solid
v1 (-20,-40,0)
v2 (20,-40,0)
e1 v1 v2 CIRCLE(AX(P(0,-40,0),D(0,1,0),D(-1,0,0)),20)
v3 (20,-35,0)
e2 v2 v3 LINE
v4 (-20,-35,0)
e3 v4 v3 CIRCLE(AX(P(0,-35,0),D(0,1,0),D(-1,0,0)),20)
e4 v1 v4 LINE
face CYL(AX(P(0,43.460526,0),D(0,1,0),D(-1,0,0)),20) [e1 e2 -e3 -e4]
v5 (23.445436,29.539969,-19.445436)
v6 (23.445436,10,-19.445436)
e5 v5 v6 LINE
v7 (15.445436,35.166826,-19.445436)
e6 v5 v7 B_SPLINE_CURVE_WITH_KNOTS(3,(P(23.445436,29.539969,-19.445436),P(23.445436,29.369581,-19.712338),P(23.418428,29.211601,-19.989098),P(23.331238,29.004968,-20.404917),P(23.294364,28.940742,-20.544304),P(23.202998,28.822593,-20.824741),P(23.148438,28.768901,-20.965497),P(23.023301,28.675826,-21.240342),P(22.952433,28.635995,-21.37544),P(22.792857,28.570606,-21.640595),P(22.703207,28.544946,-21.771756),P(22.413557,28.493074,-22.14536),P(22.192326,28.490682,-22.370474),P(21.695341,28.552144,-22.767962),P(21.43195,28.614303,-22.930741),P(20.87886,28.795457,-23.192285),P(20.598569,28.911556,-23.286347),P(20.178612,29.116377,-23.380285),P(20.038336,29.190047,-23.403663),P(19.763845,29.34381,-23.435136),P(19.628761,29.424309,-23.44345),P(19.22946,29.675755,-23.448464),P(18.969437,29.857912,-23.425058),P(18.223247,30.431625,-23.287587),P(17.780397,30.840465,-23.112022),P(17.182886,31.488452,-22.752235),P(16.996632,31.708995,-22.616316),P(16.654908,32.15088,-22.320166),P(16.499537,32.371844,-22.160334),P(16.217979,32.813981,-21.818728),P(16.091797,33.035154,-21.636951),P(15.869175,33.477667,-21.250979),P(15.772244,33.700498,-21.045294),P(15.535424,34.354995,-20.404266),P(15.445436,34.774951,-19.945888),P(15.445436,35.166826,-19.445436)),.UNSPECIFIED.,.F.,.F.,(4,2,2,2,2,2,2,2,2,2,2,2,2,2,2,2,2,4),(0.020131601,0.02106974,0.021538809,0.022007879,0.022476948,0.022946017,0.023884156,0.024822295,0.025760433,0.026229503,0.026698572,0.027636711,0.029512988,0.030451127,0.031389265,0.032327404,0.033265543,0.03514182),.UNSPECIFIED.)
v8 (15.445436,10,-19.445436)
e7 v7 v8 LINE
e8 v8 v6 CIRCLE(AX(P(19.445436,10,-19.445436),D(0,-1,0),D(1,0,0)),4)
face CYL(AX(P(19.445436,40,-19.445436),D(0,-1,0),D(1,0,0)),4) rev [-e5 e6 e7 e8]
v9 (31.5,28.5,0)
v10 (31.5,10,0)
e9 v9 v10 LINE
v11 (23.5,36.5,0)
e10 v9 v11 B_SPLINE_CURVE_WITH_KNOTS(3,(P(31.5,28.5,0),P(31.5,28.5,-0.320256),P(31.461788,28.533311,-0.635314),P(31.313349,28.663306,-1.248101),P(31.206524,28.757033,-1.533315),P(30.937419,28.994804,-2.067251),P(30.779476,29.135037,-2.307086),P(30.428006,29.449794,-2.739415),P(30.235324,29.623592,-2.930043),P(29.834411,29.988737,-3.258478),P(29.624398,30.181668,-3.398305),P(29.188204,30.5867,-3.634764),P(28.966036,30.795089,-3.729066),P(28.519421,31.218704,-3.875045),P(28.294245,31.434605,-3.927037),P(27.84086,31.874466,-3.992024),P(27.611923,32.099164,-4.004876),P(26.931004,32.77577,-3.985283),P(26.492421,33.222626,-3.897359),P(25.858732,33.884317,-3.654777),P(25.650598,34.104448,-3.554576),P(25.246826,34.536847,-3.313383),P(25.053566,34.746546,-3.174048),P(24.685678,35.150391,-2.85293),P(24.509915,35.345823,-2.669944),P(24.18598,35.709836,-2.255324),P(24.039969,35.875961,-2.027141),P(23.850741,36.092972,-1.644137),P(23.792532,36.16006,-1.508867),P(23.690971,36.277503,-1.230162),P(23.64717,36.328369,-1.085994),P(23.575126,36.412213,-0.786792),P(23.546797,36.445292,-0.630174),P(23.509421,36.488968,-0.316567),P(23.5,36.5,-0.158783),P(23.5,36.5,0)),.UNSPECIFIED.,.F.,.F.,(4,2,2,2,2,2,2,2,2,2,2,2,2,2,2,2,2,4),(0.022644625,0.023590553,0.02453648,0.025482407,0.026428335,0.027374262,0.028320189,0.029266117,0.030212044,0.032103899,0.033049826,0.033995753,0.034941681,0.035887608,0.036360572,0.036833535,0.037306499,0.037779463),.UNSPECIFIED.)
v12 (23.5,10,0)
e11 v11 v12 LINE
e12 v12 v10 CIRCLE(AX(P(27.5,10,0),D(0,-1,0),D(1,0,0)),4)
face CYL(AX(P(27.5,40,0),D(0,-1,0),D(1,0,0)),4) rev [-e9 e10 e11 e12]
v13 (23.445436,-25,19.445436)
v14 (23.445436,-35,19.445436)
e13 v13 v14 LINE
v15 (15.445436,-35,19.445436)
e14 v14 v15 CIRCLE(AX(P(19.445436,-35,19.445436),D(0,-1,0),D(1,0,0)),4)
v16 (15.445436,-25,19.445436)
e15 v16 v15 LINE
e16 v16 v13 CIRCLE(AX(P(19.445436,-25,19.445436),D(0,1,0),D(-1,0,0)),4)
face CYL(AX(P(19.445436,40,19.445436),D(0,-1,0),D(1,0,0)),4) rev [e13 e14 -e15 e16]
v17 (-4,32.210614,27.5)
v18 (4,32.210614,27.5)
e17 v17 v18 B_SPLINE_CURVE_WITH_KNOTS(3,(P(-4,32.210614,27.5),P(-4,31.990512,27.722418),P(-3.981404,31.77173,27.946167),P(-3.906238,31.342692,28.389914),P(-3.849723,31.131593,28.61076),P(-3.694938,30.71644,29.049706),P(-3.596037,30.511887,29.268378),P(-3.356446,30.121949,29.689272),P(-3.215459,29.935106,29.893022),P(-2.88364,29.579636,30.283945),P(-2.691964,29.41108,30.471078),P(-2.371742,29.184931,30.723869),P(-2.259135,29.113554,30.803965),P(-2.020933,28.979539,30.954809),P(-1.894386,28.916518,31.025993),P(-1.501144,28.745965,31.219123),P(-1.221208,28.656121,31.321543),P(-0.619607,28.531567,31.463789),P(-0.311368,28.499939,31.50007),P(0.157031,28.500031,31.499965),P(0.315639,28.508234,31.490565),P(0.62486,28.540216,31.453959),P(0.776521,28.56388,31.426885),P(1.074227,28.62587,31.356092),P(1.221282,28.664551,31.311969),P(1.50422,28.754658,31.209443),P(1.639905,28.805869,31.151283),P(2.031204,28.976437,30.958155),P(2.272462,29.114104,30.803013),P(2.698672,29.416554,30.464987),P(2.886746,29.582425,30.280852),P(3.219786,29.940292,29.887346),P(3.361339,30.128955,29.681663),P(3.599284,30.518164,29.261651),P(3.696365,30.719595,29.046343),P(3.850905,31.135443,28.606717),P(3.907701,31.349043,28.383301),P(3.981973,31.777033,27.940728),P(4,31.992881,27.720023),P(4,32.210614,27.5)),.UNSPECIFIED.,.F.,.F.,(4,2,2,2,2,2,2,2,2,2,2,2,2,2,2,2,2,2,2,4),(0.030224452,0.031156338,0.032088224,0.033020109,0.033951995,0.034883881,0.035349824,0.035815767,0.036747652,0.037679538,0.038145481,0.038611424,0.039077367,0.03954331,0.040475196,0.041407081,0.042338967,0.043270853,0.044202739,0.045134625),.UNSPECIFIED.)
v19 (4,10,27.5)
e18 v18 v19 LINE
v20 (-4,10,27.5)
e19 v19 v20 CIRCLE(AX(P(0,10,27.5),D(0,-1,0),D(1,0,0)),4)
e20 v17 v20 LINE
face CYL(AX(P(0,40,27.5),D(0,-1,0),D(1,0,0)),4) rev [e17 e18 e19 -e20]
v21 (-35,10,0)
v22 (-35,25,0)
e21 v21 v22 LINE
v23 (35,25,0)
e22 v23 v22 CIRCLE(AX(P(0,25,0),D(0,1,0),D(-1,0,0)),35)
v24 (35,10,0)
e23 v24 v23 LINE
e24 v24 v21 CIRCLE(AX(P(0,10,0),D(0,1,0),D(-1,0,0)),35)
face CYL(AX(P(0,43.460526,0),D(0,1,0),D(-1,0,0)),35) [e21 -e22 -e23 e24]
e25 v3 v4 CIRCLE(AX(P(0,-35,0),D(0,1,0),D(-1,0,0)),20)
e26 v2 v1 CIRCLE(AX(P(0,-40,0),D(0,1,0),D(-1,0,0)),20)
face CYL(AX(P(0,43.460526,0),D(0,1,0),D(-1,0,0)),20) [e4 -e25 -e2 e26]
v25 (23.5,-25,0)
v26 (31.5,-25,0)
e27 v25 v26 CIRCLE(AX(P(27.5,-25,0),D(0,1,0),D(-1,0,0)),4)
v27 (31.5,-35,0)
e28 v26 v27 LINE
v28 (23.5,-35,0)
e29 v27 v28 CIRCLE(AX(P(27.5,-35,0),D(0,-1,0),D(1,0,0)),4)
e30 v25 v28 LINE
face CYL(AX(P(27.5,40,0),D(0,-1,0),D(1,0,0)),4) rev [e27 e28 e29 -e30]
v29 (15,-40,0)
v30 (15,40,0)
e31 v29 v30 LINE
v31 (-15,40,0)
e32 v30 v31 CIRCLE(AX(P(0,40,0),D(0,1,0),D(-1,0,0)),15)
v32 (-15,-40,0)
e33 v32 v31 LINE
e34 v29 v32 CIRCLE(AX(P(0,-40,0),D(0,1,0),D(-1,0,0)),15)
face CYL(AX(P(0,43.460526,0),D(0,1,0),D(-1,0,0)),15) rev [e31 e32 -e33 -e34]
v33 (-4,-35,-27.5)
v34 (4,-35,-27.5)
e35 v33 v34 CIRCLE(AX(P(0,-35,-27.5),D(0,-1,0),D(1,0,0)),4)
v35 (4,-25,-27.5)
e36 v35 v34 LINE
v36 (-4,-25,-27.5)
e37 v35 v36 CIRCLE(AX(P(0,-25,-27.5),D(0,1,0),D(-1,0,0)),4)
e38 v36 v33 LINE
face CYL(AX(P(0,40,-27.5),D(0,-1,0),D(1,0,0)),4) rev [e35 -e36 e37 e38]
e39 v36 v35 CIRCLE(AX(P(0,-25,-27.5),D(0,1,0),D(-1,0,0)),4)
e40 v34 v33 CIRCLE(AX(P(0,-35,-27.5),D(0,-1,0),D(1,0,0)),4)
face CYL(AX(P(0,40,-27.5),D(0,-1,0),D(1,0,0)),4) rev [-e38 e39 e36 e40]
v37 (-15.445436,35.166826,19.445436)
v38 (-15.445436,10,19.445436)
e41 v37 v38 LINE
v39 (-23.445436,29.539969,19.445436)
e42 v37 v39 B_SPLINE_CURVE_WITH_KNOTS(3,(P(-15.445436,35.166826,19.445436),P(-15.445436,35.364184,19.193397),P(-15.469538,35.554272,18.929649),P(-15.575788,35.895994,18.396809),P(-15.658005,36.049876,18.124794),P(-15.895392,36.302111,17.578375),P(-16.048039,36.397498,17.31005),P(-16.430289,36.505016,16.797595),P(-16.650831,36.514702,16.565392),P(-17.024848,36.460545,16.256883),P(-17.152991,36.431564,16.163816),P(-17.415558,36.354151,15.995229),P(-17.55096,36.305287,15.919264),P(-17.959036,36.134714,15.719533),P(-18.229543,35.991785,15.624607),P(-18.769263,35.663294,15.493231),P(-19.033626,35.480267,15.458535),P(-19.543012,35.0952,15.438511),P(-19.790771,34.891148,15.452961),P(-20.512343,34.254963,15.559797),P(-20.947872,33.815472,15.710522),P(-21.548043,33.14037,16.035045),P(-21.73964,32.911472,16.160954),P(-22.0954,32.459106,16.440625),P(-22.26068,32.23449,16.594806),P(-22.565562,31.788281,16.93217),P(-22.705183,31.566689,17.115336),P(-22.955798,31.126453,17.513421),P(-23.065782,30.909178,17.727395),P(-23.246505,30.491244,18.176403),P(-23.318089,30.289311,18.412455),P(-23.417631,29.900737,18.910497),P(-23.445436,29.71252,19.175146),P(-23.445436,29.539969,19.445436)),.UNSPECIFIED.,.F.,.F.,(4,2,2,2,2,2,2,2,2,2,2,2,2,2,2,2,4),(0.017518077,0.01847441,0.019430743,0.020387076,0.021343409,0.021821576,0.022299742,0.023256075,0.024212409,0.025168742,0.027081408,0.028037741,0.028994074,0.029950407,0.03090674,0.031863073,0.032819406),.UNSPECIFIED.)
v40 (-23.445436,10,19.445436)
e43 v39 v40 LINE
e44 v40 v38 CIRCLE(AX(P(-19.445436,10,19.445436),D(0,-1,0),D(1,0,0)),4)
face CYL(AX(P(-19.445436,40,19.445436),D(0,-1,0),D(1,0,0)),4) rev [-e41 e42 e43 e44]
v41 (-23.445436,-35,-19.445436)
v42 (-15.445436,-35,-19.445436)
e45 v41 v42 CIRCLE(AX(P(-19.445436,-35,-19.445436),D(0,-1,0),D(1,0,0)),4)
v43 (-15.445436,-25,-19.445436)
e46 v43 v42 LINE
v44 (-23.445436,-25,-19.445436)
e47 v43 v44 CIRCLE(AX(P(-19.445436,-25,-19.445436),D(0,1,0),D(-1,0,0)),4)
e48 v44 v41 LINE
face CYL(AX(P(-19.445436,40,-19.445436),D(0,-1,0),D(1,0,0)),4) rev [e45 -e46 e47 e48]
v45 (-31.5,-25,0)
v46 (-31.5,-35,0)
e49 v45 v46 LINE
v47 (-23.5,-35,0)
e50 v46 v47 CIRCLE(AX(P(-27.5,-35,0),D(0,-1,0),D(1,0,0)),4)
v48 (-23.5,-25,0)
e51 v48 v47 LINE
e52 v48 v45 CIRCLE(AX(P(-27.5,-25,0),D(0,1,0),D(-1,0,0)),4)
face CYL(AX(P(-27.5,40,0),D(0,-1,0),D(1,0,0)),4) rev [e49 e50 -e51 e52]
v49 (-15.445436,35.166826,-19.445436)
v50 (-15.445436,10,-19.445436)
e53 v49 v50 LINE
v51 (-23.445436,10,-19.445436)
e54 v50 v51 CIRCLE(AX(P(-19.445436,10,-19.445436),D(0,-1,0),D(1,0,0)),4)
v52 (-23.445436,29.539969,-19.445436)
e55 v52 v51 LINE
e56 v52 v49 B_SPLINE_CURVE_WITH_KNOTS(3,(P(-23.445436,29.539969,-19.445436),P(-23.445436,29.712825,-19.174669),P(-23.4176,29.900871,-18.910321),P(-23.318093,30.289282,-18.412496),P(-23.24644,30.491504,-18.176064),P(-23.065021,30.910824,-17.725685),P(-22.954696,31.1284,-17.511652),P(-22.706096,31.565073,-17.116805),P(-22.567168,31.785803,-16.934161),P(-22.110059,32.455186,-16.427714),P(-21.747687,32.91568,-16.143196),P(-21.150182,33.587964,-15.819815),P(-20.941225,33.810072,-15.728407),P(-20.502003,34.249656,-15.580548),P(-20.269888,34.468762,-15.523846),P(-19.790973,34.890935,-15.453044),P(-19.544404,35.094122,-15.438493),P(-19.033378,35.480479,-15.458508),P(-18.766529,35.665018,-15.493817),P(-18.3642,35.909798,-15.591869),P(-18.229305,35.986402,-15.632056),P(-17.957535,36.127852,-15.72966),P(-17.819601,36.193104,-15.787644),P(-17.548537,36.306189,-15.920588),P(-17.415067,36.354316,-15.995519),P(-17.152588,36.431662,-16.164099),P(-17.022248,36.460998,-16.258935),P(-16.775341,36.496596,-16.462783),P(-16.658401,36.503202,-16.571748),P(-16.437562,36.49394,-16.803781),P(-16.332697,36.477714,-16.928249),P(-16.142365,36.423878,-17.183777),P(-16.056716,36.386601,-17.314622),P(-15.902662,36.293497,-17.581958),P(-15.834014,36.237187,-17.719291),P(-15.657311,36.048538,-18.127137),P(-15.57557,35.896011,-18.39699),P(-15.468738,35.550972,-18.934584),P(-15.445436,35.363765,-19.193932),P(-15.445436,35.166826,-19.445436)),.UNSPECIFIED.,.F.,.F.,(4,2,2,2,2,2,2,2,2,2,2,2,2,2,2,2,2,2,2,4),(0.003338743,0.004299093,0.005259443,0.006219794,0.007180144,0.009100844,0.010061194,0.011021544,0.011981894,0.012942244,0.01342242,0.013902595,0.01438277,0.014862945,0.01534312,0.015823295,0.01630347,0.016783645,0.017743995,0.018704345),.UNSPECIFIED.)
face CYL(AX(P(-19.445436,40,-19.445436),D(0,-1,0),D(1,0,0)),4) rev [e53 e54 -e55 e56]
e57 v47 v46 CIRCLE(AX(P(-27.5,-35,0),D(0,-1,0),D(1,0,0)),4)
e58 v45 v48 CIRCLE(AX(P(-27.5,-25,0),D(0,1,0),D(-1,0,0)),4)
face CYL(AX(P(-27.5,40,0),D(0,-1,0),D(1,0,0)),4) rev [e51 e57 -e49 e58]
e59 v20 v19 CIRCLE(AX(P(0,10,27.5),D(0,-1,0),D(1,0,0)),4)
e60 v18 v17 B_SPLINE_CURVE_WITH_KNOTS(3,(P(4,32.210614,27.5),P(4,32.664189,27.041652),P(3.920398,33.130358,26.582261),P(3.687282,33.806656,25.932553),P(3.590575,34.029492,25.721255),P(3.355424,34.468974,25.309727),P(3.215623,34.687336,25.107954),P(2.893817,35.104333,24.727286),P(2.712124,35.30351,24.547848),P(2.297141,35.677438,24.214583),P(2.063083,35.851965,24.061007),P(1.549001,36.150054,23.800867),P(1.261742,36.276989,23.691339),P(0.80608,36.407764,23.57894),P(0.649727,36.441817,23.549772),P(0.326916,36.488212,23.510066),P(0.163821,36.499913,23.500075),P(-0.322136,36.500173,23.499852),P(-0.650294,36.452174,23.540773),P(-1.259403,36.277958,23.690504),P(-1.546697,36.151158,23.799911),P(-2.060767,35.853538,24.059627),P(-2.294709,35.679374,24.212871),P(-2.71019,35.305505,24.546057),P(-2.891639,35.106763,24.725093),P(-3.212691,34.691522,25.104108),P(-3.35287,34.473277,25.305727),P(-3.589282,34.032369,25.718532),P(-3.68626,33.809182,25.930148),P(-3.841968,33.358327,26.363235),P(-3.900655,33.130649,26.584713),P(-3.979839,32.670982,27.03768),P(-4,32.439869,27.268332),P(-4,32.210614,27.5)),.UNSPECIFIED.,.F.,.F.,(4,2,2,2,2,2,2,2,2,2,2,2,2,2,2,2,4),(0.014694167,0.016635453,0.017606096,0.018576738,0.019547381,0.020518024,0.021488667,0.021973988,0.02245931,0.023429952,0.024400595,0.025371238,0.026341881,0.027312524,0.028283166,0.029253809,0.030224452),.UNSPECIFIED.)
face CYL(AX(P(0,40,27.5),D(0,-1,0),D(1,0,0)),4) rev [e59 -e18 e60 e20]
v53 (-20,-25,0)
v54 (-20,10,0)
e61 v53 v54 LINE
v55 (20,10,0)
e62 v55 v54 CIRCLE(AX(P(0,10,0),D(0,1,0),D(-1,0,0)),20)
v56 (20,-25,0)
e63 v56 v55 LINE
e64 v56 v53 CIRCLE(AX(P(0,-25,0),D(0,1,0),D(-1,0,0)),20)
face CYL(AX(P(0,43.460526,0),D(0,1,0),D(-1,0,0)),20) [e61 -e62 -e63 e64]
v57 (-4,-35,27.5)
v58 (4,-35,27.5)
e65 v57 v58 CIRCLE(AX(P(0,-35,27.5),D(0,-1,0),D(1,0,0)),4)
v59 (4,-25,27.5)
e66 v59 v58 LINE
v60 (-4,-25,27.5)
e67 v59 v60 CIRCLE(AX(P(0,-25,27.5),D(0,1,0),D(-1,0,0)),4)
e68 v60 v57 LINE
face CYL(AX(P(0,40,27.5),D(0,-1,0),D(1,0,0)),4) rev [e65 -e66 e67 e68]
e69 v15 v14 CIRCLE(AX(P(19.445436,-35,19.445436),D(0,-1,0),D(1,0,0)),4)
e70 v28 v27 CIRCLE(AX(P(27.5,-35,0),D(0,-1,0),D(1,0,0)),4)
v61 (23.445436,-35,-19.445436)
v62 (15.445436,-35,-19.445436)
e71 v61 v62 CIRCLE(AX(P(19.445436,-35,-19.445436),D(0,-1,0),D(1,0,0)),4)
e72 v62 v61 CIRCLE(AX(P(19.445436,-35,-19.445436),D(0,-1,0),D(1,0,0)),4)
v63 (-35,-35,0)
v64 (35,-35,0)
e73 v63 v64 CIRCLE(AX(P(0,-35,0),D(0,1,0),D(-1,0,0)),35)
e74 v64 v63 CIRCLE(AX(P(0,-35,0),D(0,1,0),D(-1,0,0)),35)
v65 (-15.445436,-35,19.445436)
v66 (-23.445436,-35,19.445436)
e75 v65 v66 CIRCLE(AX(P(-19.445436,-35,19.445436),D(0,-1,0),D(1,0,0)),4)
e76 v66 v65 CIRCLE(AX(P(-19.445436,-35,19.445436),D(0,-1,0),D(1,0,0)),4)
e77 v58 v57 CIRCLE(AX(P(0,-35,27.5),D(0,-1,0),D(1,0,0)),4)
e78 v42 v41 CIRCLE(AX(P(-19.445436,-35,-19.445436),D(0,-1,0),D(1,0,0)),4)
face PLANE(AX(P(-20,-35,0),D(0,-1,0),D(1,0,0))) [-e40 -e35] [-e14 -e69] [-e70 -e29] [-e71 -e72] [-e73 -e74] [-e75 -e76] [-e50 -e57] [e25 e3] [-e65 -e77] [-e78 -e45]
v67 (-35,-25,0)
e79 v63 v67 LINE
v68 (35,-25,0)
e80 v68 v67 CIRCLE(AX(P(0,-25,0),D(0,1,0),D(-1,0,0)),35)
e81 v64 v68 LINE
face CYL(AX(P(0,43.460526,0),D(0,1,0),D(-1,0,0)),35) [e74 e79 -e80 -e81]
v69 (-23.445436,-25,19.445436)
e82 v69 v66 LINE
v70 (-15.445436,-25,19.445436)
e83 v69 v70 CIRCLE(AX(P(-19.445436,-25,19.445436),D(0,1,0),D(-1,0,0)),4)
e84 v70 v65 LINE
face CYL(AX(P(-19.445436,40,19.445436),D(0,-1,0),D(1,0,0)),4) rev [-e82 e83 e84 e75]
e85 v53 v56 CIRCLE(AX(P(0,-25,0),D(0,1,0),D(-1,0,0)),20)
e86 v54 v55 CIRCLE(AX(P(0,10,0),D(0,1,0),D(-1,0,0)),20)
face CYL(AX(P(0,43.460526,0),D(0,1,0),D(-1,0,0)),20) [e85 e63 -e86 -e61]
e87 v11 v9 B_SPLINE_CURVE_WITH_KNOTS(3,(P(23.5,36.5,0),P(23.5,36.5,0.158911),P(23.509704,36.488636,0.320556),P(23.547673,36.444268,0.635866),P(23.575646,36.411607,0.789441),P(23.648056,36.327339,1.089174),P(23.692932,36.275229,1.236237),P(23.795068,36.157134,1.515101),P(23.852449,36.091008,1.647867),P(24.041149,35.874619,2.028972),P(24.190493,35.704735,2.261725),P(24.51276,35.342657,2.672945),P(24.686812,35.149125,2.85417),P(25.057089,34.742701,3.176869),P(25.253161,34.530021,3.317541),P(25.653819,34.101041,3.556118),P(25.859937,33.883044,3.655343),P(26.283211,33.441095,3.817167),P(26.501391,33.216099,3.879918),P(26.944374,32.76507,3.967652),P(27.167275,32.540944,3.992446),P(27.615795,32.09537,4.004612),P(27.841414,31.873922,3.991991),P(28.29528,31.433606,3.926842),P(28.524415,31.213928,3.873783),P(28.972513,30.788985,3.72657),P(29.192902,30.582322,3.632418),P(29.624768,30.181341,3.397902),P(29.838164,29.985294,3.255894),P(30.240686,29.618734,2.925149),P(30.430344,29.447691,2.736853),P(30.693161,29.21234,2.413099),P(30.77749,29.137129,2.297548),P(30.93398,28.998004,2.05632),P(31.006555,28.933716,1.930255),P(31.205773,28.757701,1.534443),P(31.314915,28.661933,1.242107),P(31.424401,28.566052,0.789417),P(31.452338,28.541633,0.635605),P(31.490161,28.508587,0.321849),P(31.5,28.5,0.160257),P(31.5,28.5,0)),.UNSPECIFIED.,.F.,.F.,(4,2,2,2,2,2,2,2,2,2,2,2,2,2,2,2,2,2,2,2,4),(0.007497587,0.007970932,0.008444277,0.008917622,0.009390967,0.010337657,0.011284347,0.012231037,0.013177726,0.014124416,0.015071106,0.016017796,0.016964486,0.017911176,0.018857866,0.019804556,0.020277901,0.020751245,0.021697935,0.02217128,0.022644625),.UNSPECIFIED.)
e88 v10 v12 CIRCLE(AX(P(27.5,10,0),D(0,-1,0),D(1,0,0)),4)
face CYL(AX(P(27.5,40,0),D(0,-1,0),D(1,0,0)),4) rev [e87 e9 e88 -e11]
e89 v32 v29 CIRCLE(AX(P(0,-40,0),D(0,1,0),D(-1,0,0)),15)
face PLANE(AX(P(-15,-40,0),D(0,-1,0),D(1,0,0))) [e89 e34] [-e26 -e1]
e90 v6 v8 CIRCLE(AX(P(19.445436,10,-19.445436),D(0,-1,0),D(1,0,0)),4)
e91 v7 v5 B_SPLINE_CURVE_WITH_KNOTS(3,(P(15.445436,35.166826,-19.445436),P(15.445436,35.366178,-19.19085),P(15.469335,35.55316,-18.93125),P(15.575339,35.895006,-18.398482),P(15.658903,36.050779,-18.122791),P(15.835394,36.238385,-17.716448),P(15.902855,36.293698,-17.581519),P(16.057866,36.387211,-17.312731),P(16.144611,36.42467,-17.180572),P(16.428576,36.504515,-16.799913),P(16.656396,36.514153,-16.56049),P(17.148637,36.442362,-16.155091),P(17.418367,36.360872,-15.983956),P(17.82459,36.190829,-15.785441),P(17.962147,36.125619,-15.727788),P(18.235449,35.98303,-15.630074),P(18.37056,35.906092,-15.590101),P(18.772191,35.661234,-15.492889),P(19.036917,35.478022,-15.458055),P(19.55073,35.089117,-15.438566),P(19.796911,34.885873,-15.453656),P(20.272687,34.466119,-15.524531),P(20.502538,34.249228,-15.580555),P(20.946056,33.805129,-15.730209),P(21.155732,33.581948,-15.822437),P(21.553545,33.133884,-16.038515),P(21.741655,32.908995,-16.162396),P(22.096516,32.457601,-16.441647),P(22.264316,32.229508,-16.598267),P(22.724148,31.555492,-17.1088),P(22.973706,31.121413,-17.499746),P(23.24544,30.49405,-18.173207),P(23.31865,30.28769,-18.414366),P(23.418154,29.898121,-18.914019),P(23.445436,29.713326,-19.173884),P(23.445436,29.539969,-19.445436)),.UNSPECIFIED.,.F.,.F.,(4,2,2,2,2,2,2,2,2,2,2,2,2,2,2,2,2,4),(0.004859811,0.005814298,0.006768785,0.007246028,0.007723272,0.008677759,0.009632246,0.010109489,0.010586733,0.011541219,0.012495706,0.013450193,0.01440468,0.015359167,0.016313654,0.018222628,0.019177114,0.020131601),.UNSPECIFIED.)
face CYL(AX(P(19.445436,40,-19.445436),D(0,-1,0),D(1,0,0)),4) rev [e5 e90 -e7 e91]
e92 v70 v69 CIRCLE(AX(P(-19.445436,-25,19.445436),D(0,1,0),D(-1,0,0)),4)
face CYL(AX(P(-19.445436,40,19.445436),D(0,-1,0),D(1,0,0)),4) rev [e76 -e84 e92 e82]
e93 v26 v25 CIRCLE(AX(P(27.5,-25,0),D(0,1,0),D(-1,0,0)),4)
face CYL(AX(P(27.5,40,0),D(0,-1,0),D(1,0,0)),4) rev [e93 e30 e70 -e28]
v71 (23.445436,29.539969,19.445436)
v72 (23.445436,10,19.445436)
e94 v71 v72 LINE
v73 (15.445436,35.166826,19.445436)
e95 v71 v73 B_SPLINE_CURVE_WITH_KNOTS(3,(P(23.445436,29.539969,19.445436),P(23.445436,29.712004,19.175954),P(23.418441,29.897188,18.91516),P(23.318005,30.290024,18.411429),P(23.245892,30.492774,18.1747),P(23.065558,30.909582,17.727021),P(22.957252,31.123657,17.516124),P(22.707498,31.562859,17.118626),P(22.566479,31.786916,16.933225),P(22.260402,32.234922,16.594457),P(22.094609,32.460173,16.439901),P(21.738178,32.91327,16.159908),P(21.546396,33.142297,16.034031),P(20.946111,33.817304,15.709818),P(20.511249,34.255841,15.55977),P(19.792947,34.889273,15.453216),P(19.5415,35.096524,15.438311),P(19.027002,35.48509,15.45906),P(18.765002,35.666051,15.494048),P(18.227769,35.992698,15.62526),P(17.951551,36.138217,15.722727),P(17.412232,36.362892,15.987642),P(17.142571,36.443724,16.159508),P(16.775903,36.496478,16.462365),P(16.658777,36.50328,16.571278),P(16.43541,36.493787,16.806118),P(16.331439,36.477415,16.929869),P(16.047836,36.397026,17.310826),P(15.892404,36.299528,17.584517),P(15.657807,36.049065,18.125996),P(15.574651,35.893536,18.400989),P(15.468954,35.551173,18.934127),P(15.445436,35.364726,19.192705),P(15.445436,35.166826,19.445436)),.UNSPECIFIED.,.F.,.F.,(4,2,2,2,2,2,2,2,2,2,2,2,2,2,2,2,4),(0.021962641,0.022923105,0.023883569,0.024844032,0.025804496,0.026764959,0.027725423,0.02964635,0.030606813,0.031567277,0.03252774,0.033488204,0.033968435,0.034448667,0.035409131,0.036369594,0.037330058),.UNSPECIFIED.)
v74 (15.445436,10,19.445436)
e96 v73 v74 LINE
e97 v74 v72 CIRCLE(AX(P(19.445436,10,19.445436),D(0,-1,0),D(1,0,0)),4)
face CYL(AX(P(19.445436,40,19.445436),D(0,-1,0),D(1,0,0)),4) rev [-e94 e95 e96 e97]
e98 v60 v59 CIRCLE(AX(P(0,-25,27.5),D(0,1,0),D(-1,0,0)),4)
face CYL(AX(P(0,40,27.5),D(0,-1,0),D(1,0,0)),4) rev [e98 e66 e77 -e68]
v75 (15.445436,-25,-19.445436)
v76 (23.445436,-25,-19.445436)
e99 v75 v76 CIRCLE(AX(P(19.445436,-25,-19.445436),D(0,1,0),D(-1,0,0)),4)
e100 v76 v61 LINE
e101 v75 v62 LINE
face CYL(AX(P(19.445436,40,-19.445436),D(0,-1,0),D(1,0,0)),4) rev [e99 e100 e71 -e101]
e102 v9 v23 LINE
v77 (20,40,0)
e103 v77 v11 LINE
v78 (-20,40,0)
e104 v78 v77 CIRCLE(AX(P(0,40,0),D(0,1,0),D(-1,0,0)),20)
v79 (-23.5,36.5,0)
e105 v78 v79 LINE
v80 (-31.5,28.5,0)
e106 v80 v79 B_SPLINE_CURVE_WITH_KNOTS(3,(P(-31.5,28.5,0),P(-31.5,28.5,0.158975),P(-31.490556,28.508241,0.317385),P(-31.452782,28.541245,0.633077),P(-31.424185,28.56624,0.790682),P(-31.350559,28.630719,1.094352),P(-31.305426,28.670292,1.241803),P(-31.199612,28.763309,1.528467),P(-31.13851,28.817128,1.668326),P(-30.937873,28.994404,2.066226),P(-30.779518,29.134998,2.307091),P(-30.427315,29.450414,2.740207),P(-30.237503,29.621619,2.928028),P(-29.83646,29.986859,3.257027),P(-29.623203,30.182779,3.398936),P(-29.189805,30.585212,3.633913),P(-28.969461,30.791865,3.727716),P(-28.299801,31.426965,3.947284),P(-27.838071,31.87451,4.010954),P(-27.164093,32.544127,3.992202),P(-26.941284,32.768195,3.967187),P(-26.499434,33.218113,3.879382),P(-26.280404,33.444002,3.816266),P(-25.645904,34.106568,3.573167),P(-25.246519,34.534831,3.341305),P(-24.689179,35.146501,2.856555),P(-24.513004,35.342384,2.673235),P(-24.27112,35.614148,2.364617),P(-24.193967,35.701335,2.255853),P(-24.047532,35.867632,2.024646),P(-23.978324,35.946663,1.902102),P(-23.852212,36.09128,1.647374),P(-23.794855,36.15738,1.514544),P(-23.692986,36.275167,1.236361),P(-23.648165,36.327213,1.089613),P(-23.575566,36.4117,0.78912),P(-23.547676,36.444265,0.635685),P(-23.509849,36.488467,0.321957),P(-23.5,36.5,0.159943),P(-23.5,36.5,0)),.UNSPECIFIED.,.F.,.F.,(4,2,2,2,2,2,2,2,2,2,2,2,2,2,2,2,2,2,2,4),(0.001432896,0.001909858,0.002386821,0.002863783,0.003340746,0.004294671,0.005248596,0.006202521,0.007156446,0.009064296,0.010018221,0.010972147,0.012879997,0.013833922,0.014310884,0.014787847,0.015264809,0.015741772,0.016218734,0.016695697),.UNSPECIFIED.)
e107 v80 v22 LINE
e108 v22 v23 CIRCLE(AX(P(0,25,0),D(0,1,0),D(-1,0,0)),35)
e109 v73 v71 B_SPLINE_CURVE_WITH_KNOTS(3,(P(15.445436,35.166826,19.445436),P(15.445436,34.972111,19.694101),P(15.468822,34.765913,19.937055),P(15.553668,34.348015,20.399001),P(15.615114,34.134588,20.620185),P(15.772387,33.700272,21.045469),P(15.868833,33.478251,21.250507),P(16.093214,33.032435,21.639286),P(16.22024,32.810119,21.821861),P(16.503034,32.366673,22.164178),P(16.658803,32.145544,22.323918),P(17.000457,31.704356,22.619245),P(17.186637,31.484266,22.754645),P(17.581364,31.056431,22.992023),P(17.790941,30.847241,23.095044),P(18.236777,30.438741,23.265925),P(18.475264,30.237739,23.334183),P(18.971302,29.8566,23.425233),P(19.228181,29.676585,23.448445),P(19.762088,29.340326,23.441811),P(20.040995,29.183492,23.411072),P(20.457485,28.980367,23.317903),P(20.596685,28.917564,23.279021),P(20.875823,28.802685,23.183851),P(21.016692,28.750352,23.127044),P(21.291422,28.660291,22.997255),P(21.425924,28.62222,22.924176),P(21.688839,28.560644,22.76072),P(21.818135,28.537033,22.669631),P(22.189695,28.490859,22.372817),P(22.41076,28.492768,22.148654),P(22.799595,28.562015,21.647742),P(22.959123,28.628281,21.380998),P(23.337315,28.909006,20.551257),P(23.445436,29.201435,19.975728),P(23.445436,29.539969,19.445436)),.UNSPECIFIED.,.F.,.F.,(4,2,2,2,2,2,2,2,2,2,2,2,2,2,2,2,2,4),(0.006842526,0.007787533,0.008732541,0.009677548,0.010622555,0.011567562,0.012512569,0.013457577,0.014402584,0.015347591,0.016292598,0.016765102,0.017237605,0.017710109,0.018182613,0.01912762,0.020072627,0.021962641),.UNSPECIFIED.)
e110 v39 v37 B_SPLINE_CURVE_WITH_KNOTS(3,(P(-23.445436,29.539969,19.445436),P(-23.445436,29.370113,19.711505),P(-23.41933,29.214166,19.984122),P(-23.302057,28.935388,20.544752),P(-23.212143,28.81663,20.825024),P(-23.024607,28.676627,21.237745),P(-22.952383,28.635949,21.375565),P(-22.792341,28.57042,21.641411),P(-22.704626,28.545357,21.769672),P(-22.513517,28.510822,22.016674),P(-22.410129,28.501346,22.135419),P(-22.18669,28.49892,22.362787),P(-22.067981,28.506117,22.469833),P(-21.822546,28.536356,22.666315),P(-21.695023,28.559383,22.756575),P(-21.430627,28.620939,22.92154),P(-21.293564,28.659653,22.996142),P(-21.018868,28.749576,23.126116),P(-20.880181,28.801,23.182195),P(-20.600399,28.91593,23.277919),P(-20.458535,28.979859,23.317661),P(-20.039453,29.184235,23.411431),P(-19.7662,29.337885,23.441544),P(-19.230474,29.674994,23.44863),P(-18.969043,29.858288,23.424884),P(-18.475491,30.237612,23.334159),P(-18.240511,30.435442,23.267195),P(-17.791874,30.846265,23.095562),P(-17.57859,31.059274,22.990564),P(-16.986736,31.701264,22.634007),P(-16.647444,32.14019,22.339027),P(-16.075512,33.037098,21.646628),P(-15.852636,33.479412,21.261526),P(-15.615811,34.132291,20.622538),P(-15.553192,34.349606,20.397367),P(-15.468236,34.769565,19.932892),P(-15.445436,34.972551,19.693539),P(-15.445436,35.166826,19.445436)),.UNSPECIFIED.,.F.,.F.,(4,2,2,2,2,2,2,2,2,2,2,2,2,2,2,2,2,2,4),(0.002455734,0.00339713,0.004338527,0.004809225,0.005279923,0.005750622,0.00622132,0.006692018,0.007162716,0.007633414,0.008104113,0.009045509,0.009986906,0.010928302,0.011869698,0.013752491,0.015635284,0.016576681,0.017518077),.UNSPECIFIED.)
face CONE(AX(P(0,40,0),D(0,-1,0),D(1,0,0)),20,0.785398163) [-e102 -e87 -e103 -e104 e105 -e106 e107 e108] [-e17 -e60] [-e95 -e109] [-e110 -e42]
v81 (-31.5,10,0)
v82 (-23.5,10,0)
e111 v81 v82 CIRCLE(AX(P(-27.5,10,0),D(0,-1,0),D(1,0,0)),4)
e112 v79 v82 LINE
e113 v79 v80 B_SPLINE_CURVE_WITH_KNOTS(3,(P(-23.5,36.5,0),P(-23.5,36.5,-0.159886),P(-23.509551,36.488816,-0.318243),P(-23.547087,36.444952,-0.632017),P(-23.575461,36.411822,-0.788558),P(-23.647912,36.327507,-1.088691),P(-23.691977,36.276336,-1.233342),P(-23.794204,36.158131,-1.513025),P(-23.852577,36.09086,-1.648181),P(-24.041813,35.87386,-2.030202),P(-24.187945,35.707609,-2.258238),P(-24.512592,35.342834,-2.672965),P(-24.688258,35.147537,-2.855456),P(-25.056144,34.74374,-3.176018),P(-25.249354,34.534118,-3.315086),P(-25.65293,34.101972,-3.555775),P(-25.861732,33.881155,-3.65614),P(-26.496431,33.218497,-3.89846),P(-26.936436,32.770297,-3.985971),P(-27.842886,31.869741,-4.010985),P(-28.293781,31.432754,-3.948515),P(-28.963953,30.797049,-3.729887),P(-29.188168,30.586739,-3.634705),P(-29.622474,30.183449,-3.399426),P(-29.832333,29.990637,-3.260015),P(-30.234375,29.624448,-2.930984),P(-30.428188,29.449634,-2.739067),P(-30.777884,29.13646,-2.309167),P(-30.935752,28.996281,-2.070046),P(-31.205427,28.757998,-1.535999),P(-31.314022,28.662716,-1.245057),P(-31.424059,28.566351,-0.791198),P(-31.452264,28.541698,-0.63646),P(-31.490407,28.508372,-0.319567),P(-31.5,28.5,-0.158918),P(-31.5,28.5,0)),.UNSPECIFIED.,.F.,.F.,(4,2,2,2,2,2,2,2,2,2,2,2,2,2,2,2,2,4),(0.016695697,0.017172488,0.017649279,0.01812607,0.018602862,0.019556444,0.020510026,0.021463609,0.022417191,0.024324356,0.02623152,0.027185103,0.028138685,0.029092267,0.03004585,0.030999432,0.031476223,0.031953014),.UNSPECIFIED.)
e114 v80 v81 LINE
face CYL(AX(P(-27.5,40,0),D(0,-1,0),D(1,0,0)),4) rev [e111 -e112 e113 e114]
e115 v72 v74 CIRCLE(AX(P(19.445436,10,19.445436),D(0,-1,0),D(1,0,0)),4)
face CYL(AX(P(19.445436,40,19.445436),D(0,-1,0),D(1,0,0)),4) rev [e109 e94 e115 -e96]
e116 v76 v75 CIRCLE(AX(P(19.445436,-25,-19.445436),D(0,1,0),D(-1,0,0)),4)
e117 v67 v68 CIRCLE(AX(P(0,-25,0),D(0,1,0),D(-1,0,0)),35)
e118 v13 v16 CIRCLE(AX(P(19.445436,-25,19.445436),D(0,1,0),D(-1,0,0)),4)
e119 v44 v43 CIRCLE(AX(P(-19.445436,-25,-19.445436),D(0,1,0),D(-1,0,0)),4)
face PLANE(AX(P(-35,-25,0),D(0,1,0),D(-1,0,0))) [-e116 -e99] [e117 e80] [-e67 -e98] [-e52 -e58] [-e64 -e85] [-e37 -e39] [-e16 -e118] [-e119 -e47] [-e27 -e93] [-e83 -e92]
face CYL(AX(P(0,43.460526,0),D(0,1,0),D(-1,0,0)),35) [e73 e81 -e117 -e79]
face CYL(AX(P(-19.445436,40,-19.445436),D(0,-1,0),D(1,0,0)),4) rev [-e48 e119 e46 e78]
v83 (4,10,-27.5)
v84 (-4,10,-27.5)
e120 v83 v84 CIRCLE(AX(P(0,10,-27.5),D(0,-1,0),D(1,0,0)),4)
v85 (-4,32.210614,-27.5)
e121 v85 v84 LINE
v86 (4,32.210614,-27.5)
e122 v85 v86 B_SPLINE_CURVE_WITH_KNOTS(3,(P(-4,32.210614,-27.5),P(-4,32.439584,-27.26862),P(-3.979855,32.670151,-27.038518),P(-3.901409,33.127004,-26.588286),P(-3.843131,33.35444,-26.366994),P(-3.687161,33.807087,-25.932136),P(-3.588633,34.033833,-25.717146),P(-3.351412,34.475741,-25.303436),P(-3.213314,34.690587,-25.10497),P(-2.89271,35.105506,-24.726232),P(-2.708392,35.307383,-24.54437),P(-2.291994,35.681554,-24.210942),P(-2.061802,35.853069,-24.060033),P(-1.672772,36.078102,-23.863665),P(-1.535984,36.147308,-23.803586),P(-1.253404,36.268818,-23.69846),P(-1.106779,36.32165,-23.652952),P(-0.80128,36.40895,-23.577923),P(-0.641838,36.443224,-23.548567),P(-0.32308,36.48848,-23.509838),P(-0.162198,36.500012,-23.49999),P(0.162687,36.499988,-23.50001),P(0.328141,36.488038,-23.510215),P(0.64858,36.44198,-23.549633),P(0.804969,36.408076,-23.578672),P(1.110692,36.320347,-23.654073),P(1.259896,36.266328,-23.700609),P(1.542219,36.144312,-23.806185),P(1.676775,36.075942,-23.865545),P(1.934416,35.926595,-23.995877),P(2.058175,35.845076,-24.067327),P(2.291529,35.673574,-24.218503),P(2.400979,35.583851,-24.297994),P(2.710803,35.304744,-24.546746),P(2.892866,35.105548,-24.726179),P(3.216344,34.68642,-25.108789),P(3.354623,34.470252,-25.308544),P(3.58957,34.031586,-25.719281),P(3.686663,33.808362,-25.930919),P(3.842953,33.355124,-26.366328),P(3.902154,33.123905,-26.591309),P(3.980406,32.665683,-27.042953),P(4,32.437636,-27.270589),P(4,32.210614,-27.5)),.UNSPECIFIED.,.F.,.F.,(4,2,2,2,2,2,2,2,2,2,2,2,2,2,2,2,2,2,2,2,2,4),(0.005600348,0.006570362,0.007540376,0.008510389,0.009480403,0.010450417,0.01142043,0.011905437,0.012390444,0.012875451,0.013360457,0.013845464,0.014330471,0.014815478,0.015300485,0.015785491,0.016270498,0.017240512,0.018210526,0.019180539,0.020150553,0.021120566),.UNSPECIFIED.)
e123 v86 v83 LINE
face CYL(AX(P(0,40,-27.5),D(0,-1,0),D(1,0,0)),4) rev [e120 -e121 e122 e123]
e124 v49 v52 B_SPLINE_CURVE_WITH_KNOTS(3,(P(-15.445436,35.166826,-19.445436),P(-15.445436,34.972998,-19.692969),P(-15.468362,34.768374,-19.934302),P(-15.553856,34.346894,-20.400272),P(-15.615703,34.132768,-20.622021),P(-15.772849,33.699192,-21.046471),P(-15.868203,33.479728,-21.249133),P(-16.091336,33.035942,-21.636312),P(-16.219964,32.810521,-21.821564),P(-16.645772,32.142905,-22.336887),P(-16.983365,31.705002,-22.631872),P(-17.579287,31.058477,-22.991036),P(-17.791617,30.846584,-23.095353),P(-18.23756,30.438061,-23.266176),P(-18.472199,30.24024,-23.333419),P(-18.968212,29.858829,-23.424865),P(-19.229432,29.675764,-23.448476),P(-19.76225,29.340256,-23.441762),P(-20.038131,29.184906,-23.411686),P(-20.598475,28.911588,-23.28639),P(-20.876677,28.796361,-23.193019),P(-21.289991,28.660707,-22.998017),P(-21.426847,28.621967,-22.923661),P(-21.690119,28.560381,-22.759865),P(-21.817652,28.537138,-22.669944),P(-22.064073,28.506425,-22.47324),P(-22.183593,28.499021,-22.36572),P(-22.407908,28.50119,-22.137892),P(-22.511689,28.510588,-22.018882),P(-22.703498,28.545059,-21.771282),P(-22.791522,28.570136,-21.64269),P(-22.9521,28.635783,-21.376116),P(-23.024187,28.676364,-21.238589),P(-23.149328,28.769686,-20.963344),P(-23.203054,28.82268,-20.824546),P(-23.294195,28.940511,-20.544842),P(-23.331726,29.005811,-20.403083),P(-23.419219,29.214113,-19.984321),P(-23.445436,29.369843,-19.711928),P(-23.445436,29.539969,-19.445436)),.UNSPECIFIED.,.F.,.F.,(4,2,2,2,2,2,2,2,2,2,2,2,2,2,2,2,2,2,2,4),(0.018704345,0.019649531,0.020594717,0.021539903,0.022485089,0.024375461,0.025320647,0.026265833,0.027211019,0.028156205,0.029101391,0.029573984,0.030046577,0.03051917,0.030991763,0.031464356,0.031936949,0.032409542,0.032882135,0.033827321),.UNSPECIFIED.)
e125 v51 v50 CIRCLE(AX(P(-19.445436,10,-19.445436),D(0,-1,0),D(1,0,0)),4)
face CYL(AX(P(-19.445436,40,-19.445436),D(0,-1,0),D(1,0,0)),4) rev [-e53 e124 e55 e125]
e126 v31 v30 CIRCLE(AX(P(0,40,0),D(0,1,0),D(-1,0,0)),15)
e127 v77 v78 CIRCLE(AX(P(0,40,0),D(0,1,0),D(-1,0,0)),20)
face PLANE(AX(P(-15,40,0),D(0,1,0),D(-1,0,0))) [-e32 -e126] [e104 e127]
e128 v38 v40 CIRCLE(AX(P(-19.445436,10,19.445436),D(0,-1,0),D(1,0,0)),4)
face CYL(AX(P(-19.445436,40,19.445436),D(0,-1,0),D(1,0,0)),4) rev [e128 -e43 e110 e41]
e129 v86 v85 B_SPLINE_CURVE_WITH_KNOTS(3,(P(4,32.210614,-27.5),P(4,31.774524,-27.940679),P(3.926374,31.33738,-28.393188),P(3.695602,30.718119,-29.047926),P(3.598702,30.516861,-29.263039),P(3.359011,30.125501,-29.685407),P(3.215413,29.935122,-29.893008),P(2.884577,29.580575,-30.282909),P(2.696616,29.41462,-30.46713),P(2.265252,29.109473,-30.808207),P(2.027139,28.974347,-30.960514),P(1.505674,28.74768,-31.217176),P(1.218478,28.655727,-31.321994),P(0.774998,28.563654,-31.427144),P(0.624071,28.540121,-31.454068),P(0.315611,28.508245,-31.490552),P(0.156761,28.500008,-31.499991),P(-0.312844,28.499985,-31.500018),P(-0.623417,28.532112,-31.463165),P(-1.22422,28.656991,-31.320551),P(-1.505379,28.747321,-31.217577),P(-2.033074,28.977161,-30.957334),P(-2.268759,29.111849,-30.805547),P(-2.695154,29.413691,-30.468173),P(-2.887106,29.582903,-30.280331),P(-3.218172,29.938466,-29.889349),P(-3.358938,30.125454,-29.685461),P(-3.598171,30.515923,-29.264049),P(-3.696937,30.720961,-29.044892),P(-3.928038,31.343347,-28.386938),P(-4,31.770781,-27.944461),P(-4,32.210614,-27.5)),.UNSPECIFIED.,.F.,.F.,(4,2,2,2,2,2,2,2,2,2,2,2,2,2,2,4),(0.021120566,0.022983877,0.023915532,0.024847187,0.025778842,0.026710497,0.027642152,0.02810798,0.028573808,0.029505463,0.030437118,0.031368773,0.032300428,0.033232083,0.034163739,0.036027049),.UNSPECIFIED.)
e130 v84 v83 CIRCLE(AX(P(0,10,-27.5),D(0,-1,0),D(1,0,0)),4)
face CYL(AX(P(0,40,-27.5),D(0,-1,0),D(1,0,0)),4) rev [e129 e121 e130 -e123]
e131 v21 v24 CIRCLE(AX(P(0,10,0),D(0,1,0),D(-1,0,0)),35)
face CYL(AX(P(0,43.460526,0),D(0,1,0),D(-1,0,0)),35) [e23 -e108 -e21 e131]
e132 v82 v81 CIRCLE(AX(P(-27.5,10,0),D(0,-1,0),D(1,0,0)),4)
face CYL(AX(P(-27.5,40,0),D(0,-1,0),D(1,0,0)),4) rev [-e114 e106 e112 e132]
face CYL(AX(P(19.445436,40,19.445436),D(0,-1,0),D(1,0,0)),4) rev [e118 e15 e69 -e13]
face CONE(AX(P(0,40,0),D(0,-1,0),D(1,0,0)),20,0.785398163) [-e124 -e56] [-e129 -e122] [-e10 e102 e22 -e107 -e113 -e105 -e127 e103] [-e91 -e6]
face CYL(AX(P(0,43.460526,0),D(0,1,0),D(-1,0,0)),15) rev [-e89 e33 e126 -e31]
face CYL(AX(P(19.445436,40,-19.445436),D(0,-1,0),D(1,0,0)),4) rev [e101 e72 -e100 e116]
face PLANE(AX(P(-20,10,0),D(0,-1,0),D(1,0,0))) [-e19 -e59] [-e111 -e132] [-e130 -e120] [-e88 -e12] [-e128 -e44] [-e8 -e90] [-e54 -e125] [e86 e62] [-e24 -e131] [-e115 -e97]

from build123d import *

# Parameters (mm, degrees)
BOLT_HOLES_8X_8_DEPTH      = 90.861003778
BOLT_HOLES_8X_8_DEPTH_BACK = 90.861003778
BOLT_HOLE_CIRCLE_SKETCH_R  = 4


with BuildPart() as part:
    # Hub Profile Sketch → Flanged Hub Body (revolve)
    with BuildSketch(Plane.XY):
        Polygon((-15, 40), (-15, -40), (-20, -40), (-20, -35), (-35, -35), (-35, -25), (-20, -25), (-20, 10), (-35, 10), (-35, 25), (-20, 40), align=None)
    revolve(axis=Axis((0, 43.460526316, 0), (0, -1, 0)))

    # Bolt Hole Circle Sketch → Bolt Holes 8xØ8 (cut, two sides: drawn at the far end of the back side and taken through both)
    with BuildSketch(Plane.XZ.offset(35).offset(-BOLT_HOLES_8X_8_DEPTH_BACK)):
        with Locations((27.5, 0)):
            Circle(BOLT_HOLE_CIRCLE_SKETCH_R)
        with Locations((19.445436483, -19.445436483)):
            Circle(BOLT_HOLE_CIRCLE_SKETCH_R)
        with Locations((0, -27.5)):
            Circle(BOLT_HOLE_CIRCLE_SKETCH_R)
        with Locations((-19.445436483, -19.445436483)):
            Circle(BOLT_HOLE_CIRCLE_SKETCH_R)
        with Locations((-27.5, 0)):
            Circle(BOLT_HOLE_CIRCLE_SKETCH_R)
        with Locations((-19.445436483, 19.445436483)):
            Circle(BOLT_HOLE_CIRCLE_SKETCH_R)
        with Locations((0, 27.5)):
            Circle(BOLT_HOLE_CIRCLE_SKETCH_R)
        with Locations((19.445436483, 19.445436483)):
            Circle(BOLT_HOLE_CIRCLE_SKETCH_R)
    extrude(amount=BOLT_HOLES_8X_8_DEPTH + BOLT_HOLES_8X_8_DEPTH_BACK, mode=Mode.SUBTRACT)


solid = part.part
